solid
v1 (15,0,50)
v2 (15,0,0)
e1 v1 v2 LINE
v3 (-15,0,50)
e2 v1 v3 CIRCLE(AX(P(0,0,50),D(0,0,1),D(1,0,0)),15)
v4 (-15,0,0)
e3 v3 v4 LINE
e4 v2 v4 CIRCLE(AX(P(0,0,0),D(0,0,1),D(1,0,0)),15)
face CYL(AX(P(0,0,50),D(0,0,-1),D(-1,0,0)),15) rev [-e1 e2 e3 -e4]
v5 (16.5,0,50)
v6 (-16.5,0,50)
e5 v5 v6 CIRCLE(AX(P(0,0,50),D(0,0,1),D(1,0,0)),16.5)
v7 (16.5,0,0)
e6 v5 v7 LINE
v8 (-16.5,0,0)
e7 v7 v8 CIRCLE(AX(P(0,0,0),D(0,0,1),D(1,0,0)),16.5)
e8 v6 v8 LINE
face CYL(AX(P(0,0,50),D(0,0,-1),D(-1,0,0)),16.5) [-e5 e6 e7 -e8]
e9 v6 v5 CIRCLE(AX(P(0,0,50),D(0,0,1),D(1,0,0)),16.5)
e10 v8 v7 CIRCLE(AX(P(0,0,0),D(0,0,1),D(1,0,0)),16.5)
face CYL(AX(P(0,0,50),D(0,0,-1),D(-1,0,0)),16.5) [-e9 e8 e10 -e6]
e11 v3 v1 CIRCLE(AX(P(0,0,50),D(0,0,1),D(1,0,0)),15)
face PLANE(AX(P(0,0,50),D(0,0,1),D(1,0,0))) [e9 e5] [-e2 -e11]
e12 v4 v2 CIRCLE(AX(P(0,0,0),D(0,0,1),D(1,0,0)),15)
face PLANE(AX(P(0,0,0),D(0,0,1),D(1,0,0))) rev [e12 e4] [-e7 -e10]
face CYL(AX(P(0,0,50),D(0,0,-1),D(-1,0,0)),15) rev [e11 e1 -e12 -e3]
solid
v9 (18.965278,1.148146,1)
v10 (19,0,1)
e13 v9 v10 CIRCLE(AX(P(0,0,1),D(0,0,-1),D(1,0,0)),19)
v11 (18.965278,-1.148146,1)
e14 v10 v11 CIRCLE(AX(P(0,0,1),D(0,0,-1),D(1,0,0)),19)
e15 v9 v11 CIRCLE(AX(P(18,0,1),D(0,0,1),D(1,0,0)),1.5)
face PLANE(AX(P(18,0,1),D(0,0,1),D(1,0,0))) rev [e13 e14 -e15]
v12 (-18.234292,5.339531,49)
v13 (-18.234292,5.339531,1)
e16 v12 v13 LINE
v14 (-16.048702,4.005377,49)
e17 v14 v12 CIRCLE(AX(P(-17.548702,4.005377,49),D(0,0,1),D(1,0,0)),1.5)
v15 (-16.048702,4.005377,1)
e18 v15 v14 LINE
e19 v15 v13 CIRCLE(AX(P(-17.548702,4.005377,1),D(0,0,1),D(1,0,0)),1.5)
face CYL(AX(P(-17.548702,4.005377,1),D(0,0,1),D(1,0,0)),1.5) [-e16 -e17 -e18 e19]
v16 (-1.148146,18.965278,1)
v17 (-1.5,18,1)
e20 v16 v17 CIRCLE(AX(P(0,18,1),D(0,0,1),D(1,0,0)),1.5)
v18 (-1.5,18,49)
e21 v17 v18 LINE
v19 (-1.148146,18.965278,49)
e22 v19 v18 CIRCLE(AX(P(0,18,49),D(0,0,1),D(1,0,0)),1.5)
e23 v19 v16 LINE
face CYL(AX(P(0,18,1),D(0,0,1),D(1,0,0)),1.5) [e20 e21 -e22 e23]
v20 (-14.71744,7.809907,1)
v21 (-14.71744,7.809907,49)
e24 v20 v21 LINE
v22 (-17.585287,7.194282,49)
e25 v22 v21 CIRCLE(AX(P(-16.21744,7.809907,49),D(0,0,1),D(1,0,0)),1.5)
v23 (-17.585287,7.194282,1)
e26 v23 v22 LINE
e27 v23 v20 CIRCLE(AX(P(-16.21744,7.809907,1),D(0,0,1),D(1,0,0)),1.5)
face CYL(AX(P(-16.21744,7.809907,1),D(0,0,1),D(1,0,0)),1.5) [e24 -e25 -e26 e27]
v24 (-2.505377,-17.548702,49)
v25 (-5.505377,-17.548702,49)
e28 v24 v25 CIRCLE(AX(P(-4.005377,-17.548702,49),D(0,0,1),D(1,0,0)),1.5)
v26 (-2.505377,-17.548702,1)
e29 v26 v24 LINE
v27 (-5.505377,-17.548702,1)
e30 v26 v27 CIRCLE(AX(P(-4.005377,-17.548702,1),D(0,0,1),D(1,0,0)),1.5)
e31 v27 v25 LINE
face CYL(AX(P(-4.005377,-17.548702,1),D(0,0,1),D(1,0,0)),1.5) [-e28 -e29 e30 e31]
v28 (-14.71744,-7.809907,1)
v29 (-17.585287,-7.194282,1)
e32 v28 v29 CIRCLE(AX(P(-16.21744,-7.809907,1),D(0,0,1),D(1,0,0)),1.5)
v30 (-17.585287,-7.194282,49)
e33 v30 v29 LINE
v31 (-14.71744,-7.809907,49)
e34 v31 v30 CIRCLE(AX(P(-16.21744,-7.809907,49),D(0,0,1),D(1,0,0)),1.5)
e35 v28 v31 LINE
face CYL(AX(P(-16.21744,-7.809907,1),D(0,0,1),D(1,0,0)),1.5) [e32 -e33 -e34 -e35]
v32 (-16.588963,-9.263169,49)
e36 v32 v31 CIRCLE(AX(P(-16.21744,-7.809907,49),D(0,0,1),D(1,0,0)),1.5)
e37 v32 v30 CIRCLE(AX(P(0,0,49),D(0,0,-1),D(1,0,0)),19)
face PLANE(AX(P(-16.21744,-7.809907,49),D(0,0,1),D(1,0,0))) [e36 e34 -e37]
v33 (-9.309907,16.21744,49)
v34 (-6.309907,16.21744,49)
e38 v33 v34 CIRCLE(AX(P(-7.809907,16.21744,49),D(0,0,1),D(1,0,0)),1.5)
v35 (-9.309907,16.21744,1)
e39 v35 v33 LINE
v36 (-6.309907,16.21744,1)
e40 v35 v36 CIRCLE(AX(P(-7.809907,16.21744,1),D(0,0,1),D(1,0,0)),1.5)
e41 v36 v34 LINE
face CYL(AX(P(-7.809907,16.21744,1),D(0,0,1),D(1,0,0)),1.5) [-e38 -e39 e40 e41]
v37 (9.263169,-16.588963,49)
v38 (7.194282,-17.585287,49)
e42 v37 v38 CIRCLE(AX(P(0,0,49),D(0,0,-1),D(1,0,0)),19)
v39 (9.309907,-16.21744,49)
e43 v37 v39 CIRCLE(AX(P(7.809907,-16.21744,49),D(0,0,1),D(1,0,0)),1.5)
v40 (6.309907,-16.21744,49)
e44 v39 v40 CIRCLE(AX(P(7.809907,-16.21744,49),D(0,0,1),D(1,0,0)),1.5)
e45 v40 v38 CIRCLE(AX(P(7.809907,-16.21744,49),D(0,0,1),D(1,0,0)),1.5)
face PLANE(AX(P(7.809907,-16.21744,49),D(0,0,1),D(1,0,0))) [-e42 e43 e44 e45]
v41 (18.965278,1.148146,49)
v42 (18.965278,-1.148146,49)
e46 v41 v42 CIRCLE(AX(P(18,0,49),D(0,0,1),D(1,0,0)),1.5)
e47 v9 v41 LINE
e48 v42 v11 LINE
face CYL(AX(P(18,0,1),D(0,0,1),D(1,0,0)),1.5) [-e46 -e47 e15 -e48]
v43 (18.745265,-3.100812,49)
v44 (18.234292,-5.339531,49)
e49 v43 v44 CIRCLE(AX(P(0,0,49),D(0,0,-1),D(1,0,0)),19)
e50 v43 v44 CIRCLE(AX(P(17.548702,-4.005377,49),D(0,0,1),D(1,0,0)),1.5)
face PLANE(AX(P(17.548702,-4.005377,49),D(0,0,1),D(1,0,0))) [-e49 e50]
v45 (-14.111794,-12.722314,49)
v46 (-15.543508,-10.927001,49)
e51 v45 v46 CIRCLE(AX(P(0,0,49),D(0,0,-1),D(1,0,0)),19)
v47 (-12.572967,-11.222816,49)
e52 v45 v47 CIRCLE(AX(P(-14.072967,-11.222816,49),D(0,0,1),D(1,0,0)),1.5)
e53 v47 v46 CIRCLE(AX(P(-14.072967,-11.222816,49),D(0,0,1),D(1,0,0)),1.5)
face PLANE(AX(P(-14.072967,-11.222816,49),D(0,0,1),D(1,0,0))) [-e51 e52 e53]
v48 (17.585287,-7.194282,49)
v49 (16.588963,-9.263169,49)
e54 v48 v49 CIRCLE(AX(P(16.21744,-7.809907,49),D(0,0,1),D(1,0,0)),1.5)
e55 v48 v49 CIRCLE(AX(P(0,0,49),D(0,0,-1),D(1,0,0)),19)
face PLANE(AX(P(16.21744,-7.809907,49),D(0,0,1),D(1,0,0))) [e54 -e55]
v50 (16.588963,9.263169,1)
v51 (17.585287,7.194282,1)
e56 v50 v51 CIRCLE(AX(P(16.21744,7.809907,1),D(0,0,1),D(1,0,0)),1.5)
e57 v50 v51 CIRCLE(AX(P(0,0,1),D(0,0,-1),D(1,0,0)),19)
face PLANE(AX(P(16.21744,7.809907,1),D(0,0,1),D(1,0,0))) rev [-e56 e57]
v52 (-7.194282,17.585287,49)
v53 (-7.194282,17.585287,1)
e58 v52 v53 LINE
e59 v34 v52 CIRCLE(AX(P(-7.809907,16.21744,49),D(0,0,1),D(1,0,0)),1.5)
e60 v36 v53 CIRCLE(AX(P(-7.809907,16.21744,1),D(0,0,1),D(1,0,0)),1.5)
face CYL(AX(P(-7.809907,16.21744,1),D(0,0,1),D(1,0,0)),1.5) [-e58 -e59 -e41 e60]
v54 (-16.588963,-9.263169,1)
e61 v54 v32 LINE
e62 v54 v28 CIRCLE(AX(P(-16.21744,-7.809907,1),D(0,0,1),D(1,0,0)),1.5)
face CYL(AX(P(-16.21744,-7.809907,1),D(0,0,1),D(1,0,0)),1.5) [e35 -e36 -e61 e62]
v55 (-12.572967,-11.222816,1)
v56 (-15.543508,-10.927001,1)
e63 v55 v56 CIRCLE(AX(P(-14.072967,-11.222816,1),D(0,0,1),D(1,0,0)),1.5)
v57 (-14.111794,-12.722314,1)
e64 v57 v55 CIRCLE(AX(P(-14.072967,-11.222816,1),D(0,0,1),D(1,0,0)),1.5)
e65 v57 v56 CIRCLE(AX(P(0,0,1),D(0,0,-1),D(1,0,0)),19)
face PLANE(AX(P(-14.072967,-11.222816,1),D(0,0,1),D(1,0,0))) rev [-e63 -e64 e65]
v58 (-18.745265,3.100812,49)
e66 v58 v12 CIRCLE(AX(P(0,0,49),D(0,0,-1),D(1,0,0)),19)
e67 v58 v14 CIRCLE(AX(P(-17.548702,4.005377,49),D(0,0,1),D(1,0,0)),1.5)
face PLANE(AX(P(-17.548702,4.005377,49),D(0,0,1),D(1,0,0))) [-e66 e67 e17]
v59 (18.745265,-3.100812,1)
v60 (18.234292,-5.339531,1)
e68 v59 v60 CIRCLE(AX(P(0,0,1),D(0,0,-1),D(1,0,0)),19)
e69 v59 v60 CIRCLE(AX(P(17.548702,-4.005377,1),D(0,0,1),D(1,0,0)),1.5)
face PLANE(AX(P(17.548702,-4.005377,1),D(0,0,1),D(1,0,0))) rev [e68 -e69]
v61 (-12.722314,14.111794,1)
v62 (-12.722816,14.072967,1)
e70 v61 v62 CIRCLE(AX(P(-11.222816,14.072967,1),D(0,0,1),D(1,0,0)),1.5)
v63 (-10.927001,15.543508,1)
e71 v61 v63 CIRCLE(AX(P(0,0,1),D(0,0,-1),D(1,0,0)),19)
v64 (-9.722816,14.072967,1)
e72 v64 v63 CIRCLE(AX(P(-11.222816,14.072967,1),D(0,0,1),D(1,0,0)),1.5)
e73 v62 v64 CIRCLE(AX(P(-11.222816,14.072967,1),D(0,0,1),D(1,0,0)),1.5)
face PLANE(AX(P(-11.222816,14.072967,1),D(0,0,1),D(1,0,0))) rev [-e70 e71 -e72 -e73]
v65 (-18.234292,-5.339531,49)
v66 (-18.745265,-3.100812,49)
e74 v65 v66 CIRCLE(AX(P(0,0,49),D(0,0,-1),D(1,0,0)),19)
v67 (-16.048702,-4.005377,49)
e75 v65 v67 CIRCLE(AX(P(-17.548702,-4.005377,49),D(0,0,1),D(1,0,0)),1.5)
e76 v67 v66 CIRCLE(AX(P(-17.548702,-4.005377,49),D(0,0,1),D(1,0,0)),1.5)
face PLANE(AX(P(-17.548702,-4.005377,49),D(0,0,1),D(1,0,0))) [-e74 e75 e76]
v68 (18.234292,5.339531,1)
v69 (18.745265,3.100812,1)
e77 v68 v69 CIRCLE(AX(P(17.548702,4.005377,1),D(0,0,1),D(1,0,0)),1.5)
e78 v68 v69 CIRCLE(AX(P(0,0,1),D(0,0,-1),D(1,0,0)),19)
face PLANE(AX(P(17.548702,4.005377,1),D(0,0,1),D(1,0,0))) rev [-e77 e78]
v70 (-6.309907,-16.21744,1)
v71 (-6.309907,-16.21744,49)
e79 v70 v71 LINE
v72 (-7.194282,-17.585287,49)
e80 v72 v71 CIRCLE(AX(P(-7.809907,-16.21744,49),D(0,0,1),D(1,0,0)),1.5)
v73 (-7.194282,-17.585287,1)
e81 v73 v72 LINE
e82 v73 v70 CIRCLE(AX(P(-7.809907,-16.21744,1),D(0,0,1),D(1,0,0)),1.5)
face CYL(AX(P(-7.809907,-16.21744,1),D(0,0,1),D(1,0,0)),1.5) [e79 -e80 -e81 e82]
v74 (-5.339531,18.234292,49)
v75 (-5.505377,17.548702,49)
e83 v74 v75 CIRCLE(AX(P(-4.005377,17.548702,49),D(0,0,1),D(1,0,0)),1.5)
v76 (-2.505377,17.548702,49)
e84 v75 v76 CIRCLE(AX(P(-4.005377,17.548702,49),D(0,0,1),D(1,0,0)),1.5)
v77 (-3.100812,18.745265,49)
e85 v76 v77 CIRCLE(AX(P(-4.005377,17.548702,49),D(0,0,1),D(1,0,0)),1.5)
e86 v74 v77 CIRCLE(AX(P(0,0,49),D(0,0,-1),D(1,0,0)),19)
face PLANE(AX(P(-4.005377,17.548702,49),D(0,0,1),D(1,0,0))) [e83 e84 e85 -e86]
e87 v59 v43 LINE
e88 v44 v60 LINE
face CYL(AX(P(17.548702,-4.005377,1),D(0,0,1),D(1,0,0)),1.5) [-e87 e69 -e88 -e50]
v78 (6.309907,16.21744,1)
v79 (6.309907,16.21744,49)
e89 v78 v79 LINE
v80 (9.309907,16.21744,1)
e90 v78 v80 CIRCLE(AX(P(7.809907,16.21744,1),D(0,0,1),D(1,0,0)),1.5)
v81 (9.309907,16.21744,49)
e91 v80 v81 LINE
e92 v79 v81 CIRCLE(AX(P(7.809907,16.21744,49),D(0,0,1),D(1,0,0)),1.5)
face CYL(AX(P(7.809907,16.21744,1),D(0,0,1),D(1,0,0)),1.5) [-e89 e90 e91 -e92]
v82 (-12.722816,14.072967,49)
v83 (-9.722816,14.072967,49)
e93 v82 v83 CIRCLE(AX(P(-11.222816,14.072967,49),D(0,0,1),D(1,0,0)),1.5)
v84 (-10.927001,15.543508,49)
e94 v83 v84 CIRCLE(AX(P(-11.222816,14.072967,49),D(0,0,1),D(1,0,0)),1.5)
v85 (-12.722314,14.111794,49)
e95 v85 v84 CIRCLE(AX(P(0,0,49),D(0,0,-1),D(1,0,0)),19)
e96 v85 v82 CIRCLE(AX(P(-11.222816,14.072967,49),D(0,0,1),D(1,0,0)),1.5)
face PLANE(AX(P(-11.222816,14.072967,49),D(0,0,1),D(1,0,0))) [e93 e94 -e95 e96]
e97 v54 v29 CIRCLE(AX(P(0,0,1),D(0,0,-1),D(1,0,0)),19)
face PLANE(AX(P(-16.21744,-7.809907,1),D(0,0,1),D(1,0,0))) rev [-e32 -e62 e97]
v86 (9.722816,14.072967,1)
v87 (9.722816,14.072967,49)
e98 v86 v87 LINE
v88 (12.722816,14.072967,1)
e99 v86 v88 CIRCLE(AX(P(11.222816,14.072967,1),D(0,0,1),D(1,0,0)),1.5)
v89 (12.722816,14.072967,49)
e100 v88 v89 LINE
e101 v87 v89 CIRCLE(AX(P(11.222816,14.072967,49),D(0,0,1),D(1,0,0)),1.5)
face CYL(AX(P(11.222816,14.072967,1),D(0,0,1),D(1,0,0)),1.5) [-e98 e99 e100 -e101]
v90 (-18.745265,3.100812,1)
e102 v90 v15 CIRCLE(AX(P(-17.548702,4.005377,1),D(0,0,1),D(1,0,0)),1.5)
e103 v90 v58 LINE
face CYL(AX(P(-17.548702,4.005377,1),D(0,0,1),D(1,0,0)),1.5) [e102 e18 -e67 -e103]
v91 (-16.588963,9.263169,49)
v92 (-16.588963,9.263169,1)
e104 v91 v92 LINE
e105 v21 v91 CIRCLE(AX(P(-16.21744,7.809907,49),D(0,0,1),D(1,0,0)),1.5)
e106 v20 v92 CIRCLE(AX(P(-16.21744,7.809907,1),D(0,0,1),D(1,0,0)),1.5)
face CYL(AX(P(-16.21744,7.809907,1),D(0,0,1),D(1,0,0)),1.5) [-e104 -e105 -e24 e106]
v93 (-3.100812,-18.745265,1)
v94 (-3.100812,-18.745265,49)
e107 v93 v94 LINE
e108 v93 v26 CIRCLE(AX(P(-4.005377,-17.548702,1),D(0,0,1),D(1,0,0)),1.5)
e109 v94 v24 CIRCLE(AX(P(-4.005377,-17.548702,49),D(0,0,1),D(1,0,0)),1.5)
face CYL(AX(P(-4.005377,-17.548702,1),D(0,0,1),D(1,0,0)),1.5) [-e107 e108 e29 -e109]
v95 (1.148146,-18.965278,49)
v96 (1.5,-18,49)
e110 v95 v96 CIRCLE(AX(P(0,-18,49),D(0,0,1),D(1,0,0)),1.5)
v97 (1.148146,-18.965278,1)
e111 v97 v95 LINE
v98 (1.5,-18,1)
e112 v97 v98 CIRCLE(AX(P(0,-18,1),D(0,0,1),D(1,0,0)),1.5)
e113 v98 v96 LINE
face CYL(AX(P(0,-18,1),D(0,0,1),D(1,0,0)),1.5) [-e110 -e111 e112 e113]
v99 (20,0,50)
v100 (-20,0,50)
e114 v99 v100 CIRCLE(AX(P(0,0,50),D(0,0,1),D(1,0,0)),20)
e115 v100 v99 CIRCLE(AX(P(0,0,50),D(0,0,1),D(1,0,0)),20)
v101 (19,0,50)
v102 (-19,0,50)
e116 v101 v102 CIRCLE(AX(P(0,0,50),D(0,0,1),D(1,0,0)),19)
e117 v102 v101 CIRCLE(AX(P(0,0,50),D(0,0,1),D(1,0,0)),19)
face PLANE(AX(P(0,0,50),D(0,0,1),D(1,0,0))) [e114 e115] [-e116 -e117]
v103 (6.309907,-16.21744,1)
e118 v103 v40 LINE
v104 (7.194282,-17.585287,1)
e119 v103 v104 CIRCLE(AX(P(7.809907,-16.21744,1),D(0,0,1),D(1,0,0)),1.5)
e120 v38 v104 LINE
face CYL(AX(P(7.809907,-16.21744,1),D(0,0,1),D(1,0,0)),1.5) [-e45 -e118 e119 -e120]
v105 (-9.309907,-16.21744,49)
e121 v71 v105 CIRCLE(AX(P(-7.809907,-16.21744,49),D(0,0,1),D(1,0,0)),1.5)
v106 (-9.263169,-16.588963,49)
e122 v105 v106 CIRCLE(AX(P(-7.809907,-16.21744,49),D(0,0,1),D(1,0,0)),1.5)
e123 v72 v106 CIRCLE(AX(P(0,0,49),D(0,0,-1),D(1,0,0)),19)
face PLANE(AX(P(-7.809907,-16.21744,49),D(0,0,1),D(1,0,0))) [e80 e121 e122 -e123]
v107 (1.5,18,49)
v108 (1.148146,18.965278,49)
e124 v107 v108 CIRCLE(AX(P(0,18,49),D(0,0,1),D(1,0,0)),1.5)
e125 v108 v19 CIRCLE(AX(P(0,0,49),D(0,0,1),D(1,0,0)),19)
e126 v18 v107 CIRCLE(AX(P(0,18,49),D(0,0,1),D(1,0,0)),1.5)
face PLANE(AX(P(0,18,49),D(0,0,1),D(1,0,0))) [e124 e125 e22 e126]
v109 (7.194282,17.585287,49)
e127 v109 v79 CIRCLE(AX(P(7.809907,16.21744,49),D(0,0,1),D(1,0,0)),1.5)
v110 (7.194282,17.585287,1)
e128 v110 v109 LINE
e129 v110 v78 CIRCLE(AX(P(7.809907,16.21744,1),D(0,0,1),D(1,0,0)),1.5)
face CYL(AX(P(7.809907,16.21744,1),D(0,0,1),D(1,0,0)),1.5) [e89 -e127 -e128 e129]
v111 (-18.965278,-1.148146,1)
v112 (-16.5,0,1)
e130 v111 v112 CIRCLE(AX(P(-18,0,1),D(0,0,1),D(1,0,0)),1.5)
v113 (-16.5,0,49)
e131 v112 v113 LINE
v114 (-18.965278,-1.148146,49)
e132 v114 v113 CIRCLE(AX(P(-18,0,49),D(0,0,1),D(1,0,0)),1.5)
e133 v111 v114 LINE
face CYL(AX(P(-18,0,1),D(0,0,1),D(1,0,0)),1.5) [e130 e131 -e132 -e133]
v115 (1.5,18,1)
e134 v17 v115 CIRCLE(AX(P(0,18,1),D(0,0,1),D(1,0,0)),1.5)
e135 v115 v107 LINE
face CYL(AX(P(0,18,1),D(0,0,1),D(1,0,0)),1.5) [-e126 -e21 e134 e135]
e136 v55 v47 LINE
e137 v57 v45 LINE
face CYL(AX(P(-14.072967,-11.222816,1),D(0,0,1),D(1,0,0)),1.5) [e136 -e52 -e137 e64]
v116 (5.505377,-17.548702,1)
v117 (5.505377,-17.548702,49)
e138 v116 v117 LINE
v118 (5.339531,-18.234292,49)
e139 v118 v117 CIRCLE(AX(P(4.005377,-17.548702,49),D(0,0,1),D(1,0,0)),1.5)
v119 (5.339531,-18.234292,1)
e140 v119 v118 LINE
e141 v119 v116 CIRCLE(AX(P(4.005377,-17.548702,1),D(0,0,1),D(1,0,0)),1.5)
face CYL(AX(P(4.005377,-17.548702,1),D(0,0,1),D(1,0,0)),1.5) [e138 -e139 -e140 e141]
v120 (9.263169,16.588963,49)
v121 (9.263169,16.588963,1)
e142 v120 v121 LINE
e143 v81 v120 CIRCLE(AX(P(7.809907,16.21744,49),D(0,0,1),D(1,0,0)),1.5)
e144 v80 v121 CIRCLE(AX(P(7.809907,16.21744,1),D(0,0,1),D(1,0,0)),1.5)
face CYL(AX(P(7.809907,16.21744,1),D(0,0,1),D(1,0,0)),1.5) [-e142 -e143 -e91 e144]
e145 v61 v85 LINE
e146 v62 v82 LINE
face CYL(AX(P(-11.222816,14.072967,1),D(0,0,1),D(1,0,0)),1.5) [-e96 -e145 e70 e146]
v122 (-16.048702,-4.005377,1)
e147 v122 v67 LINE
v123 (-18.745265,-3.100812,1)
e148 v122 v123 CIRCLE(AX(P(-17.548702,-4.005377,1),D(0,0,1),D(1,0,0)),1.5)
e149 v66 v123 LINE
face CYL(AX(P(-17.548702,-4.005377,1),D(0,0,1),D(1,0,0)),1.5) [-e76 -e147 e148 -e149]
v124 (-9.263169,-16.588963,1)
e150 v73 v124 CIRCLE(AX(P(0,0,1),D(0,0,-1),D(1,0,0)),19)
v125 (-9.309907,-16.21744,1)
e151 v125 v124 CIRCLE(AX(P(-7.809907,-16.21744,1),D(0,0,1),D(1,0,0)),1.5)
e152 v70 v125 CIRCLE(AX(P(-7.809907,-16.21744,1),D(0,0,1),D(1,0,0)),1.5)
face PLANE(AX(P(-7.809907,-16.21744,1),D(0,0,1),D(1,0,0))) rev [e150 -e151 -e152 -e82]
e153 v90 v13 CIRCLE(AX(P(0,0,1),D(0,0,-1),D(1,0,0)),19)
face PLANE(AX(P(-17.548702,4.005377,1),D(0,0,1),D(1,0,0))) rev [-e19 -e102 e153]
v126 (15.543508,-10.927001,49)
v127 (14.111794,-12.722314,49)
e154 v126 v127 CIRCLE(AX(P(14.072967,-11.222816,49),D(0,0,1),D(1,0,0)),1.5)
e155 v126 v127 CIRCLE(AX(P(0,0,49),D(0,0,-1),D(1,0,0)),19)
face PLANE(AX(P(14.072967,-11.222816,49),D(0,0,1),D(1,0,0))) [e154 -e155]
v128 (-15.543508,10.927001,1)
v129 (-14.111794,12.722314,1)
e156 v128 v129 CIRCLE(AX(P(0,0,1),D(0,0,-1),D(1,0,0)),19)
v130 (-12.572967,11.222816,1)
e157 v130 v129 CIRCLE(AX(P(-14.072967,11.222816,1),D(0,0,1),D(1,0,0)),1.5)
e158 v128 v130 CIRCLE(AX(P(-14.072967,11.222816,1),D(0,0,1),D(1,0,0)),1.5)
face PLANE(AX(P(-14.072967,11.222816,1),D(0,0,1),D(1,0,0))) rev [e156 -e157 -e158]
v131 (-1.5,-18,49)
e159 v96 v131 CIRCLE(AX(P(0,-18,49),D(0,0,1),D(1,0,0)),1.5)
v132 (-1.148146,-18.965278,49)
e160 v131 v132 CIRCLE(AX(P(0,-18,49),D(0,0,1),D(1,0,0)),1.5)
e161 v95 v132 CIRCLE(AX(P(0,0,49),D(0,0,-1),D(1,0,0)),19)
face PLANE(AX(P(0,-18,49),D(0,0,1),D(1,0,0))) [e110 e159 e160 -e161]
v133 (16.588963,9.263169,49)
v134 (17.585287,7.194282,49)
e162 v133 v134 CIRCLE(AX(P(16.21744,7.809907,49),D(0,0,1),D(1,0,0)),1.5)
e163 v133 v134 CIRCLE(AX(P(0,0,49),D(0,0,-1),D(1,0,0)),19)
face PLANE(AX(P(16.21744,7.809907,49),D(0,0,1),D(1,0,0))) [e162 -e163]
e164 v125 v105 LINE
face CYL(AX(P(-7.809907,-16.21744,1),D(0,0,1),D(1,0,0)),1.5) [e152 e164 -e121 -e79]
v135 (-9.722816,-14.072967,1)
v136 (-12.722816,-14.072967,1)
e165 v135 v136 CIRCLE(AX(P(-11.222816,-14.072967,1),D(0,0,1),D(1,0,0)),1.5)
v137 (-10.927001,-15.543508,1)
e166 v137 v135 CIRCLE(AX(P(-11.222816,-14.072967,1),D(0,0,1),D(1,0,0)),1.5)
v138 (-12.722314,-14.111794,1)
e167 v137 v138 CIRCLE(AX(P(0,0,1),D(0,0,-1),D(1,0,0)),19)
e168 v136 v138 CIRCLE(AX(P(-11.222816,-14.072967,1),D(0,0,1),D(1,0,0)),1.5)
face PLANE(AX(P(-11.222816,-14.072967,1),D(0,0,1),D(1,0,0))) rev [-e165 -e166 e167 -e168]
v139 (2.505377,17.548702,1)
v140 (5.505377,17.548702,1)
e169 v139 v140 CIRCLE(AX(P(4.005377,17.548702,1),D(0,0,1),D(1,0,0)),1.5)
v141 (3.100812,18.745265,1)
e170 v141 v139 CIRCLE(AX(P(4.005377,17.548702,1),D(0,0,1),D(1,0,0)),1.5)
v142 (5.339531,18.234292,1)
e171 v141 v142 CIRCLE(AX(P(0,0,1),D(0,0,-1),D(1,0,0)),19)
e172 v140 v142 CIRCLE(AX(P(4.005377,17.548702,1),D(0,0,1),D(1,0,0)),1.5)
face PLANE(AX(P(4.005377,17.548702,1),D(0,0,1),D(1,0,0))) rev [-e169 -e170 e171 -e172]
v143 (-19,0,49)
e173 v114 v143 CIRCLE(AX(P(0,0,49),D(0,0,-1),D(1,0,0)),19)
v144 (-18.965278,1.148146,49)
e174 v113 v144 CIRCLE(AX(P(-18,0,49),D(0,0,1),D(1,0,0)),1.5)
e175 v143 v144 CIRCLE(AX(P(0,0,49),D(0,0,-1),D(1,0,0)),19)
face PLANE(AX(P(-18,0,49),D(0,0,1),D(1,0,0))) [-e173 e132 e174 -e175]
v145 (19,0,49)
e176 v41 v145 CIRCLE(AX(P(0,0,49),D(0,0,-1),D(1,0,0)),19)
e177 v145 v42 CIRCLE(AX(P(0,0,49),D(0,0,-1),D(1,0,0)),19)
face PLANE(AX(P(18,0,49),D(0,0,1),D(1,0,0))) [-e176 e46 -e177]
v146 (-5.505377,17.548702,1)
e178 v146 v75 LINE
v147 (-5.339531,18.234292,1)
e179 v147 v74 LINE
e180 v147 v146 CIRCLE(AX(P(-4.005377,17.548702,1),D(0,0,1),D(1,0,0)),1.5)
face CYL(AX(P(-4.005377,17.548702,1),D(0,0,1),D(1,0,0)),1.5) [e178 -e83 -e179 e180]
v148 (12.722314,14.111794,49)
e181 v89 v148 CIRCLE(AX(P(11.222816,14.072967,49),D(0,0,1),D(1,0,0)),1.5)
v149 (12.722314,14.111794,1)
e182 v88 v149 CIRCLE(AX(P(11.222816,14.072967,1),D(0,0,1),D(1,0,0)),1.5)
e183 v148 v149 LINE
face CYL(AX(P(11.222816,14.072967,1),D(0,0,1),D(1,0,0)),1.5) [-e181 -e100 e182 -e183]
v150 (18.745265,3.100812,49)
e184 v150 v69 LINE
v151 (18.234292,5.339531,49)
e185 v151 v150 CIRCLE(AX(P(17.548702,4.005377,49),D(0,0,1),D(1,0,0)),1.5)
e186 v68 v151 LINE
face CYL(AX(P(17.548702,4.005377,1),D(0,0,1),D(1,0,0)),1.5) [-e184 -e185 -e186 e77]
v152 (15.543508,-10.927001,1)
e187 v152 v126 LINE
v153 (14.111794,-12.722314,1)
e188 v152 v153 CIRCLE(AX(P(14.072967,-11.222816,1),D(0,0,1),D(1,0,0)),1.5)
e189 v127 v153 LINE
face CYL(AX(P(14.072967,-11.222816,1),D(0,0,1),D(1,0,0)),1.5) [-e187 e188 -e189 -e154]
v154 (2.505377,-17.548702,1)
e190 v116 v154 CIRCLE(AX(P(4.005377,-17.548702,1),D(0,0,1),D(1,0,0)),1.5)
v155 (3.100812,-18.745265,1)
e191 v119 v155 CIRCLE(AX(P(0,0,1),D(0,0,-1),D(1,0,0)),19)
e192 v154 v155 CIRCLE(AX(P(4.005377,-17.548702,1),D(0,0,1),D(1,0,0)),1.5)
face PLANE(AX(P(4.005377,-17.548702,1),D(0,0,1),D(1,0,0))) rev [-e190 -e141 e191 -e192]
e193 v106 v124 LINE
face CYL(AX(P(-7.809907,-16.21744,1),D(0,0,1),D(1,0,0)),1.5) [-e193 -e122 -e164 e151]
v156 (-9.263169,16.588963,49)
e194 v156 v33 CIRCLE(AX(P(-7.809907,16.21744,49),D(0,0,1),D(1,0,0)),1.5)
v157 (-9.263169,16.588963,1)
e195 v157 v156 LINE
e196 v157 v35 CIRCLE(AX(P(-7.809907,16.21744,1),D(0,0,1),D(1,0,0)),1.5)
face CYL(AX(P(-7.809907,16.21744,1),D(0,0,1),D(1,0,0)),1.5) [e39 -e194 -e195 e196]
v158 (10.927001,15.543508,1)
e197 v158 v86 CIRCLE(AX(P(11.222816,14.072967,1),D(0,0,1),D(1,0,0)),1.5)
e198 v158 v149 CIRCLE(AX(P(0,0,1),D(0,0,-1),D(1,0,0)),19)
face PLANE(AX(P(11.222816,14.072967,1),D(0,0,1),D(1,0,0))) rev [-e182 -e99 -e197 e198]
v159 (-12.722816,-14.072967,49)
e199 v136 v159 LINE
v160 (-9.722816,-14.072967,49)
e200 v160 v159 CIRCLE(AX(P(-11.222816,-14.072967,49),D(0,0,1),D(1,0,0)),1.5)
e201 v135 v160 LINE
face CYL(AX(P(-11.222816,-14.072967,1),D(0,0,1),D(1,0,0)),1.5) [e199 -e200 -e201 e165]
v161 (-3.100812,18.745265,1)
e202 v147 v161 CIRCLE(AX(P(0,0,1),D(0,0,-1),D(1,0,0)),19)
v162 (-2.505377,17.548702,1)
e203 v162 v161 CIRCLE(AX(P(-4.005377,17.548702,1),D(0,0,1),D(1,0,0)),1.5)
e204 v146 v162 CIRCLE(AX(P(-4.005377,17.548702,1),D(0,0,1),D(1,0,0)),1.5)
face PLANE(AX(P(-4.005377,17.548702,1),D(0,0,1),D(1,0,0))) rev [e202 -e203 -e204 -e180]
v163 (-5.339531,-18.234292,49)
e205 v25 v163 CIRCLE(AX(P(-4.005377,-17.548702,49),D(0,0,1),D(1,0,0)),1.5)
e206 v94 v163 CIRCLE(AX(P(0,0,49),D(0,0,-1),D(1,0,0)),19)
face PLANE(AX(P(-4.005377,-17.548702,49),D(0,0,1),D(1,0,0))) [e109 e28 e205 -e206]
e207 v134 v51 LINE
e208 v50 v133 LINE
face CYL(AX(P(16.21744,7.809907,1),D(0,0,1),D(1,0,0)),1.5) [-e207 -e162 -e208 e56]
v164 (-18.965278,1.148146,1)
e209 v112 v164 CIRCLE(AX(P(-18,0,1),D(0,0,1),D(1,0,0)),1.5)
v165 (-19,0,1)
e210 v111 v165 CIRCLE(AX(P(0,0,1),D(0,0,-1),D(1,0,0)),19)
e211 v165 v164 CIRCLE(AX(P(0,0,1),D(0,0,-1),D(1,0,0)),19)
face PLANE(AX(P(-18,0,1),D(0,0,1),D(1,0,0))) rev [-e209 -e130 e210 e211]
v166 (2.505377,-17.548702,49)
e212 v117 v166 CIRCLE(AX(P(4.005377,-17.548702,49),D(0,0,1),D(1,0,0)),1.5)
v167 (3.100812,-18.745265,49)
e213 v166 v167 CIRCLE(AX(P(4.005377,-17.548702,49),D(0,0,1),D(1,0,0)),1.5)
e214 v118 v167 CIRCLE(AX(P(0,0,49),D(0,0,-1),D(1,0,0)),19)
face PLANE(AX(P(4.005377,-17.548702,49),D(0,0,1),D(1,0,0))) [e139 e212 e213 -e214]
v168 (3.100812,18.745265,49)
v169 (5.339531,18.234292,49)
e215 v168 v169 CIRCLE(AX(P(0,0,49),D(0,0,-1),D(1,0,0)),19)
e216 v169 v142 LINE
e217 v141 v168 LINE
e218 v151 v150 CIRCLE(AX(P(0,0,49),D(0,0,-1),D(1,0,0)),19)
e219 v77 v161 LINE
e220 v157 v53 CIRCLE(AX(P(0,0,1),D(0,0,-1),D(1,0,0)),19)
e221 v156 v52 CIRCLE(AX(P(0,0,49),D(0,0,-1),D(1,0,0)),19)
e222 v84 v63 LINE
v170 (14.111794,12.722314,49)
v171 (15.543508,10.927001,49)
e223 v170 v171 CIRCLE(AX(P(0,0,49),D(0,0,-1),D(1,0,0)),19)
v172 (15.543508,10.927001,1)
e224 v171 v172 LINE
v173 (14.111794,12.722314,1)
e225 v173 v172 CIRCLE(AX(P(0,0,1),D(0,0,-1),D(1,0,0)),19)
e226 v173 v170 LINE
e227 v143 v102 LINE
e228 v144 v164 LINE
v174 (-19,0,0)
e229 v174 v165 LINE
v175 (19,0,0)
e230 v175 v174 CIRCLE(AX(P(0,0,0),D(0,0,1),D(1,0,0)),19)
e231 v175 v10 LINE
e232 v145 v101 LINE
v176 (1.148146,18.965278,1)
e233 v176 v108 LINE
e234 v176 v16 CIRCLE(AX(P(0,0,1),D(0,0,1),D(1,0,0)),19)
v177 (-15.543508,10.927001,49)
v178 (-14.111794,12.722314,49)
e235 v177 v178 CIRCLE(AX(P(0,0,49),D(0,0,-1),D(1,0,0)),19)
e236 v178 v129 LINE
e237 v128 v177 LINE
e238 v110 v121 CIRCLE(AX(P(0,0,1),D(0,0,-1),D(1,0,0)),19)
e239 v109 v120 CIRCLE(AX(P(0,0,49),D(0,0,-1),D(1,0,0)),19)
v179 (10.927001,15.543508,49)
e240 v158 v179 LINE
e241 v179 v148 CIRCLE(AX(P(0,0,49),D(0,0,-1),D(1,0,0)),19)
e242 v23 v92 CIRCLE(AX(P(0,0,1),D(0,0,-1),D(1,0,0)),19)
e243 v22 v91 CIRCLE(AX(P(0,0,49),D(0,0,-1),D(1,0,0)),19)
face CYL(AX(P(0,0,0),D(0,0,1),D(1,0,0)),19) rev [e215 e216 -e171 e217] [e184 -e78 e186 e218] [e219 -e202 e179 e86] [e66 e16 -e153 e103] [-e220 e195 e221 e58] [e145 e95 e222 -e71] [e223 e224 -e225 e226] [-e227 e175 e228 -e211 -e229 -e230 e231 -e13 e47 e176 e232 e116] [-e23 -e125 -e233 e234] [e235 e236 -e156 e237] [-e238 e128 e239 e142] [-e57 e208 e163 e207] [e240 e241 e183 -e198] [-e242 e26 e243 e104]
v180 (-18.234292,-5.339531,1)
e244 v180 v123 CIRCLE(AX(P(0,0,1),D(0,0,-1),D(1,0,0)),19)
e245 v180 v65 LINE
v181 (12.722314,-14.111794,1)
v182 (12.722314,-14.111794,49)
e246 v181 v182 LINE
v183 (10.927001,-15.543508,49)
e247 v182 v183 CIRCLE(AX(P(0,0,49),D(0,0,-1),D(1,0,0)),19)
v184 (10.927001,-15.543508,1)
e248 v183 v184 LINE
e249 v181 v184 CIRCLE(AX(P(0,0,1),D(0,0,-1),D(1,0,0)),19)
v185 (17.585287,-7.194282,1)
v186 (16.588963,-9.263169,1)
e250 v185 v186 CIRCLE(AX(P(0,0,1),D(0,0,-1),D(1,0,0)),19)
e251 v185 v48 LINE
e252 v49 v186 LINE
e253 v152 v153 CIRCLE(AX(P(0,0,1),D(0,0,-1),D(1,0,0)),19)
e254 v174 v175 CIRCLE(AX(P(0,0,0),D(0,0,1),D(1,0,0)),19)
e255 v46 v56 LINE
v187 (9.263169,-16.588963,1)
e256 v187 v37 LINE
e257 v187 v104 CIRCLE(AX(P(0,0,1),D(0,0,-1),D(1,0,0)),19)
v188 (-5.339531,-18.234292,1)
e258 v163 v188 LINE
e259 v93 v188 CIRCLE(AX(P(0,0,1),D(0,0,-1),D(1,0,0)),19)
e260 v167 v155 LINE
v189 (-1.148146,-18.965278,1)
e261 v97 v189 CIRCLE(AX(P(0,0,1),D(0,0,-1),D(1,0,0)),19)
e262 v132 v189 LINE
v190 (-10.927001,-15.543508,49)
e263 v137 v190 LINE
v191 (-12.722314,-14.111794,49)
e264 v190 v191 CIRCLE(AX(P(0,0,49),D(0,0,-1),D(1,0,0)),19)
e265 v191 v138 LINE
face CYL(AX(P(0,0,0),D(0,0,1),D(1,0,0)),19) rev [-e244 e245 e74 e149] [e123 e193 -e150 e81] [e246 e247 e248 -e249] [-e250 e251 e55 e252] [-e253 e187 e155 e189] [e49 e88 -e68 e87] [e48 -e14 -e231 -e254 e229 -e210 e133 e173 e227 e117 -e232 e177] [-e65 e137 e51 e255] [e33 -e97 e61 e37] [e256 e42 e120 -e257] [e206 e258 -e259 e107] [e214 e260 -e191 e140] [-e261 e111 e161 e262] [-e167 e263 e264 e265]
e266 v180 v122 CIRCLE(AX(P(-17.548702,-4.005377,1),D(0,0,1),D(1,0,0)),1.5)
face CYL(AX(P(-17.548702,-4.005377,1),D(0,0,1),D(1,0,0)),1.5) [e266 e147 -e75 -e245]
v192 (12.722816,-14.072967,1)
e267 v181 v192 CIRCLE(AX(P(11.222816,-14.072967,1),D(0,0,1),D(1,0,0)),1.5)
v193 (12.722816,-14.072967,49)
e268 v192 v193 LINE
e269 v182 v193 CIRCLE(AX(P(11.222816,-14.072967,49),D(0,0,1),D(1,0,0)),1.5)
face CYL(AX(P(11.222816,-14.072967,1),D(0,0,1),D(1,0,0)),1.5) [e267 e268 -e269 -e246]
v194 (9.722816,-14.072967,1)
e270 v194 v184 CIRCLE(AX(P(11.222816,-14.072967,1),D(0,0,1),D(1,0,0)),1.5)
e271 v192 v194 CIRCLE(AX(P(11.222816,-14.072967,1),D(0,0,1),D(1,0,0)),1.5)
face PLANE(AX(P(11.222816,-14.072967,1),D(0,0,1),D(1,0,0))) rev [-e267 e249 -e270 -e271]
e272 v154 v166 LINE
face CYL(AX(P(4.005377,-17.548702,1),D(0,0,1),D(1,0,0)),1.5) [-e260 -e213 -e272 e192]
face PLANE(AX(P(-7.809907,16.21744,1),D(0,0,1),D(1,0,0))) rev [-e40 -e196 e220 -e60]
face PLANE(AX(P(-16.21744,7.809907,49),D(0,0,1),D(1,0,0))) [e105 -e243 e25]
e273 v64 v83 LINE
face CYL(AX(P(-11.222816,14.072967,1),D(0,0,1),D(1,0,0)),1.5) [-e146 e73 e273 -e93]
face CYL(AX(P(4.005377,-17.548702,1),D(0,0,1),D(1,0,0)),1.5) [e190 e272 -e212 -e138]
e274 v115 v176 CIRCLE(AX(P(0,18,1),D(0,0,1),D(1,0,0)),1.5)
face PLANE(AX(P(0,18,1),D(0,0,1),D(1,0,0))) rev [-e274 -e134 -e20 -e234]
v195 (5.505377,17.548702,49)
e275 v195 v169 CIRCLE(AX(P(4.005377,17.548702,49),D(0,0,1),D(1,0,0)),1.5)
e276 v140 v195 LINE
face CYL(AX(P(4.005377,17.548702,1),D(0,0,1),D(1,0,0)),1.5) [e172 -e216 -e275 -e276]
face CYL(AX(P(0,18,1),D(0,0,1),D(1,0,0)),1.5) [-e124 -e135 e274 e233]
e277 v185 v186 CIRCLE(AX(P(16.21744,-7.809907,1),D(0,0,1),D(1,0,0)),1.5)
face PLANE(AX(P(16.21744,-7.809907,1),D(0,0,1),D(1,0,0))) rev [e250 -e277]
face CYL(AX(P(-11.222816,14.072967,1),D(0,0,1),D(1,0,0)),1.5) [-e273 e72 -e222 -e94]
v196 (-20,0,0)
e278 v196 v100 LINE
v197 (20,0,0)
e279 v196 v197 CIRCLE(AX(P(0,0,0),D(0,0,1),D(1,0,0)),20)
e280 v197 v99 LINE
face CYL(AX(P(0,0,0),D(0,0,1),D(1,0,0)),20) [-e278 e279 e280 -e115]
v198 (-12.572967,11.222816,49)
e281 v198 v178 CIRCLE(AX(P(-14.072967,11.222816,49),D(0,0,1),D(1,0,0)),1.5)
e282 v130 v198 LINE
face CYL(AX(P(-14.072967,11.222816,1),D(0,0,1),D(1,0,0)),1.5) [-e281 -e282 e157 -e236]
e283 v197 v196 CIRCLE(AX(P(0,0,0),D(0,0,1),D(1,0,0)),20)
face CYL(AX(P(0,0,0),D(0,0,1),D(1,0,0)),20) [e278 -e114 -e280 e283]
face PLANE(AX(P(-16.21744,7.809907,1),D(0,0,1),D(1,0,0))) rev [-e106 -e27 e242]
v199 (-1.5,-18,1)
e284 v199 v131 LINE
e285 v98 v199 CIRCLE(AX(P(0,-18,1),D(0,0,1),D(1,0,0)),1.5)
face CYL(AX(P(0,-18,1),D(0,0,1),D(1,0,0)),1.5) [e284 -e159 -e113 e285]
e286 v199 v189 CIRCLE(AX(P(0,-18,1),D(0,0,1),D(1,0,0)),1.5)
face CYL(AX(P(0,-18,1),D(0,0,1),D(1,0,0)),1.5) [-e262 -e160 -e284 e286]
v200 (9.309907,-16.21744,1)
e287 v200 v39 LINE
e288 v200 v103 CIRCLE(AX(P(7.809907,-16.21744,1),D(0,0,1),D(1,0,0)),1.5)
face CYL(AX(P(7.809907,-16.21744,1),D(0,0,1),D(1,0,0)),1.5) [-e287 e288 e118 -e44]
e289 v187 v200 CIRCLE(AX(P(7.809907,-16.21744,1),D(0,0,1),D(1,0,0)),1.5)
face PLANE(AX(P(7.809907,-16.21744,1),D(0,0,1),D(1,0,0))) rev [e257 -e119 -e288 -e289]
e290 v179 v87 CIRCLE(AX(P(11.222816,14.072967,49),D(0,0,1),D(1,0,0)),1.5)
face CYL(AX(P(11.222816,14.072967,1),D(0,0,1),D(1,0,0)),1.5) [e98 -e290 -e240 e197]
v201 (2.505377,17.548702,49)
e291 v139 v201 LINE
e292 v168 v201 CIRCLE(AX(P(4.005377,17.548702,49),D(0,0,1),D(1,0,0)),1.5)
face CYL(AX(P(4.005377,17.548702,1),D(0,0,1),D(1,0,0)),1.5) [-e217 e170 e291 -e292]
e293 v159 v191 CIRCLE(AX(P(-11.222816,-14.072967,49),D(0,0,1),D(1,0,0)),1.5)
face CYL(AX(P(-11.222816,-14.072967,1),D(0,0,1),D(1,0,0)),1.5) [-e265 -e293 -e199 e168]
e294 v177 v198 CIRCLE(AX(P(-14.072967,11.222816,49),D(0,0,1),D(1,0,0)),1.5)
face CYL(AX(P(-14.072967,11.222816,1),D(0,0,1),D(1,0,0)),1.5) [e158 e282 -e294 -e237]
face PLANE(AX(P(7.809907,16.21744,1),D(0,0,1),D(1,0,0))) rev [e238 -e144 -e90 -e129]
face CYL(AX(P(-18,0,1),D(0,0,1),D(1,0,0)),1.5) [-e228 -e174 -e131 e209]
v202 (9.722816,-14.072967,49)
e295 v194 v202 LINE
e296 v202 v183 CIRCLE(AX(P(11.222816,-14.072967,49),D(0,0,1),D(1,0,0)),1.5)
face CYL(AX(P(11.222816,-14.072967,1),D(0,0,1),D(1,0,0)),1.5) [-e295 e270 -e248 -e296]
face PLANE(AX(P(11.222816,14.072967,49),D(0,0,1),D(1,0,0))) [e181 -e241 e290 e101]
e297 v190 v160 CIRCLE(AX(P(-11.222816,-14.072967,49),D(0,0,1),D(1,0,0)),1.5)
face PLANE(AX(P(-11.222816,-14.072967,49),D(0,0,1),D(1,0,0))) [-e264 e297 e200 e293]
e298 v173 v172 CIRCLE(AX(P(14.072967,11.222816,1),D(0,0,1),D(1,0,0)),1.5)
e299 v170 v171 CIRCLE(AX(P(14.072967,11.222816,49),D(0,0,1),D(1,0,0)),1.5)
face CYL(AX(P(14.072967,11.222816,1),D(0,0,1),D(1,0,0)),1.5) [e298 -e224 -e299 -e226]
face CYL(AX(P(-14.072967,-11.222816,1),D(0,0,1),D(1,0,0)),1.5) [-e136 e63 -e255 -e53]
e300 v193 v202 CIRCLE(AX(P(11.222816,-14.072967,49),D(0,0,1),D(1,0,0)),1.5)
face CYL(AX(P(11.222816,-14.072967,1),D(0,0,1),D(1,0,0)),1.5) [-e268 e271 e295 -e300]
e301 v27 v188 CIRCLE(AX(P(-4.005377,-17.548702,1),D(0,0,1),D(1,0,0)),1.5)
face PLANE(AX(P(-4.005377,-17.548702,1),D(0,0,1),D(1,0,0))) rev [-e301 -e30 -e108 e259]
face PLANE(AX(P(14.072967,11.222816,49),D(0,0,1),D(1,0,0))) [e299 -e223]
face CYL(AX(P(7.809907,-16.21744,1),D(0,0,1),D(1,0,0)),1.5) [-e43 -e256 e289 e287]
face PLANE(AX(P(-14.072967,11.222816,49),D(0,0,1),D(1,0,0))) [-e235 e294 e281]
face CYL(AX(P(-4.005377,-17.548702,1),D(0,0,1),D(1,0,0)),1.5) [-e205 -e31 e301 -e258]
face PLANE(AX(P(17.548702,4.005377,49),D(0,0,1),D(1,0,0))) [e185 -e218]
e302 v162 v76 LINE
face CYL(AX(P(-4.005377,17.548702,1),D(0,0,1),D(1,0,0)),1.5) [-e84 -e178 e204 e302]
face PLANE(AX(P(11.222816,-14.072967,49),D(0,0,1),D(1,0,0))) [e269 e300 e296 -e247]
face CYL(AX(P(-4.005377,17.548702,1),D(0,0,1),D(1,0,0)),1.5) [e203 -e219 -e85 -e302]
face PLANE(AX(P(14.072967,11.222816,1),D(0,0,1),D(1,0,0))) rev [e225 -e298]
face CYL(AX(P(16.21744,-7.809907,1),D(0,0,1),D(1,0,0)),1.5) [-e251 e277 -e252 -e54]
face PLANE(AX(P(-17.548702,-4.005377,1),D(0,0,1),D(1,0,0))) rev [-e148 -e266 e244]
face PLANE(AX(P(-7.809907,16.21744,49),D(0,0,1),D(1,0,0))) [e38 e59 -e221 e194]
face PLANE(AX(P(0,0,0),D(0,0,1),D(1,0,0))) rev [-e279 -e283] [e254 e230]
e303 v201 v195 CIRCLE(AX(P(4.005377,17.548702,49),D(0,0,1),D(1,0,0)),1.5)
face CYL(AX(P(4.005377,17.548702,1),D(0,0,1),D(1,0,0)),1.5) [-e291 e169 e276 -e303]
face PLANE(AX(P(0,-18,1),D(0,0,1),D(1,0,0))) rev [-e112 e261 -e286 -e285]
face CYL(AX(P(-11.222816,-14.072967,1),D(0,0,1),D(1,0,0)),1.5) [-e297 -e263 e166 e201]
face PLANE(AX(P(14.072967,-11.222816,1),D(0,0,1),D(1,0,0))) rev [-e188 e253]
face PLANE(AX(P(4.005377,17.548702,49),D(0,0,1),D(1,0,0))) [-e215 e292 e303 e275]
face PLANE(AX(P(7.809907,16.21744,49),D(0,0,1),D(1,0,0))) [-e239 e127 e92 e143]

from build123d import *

# Parameters (mm, degrees)
SKETCH1_R              = 16.5
SKETCH1_R_2            = 15
BOSS_EXTRUDE1_DEPTH    = 50
BOSS_EXTRUDE2_START    = -1
SKETCH2_R              = 1.5
BOSS_EXTRUDE2_DEPTH    = 48
BOSS_EXTRUDE2_2_DEPTH  = 48
BOSS_EXTRUDE2_3_DEPTH  = 48
BOSS_EXTRUDE2_4_DEPTH  = 48
BOSS_EXTRUDE2_5_DEPTH  = 48
BOSS_EXTRUDE2_6_DEPTH  = 48
BOSS_EXTRUDE2_7_DEPTH  = 48
BOSS_EXTRUDE2_8_DEPTH  = 48
BOSS_EXTRUDE2_9_DEPTH  = 48
BOSS_EXTRUDE2_10_DEPTH = 48
BOSS_EXTRUDE2_11_DEPTH = 48
BOSS_EXTRUDE2_12_DEPTH = 48
BOSS_EXTRUDE2_13_DEPTH = 48
BOSS_EXTRUDE2_14_DEPTH = 48
BOSS_EXTRUDE2_15_DEPTH = 48
BOSS_EXTRUDE2_16_DEPTH = 48
BOSS_EXTRUDE2_17_DEPTH = 48
BOSS_EXTRUDE2_18_DEPTH = 48
BOSS_EXTRUDE2_19_DEPTH = 48
BOSS_EXTRUDE2_20_DEPTH = 48
BOSS_EXTRUDE2_21_DEPTH = 48
BOSS_EXTRUDE2_22_DEPTH = 48
BOSS_EXTRUDE2_23_DEPTH = 48
BOSS_EXTRUDE2_24_DEPTH = 48
BOSS_EXTRUDE2_25_DEPTH = 48
BOSS_EXTRUDE2_26_DEPTH = 48
BOSS_EXTRUDE2_27_DEPTH = 48
BOSS_EXTRUDE2_28_DEPTH = 48
SKETCH3_R              = 20
SKETCH3_R_2            = 19
BOSS_EXTRUDE3_DEPTH    = 50


with BuildPart() as part:
    # Sketch1 → Boss-Extrude1 (new body)
    with BuildSketch(Plane.XY):
        Circle(SKETCH1_R)
        Circle(SKETCH1_R_2, mode=Mode.SUBTRACT)
    extrude(amount=BOSS_EXTRUDE1_DEPTH)


with BuildPart() as body_2:
    # Sketch2 → Boss-Extrude2 (new body)
    with BuildSketch(Plane.XY.offset(50).offset(BOSS_EXTRUDE2_START)):
        with Locations((0, 18)):
            Circle(SKETCH2_R)
    extrude(amount=-BOSS_EXTRUDE2_DEPTH)



with BuildPart() as body_3:
    # Sketch2 → Boss-Extrude2 2 (new body)
    with BuildSketch(Plane.XY.offset(50).offset(BOSS_EXTRUDE2_START)):
        with Locations((4.005376811, 17.548702419)):
            Circle(SKETCH2_R)
    extrude(amount=-BOSS_EXTRUDE2_2_DEPTH)


with BuildPart() as body_4:
    # Sketch2 → Boss-Extrude2 3 (new body)
    with BuildSketch(Plane.XY.offset(50).offset(BOSS_EXTRUDE2_START)):
        with Locations((7.809907304, 16.217439622)):
            Circle(SKETCH2_R)
    extrude(amount=-BOSS_EXTRUDE2_3_DEPTH)


with BuildPart() as body_5:
    # Sketch2 → Boss-Extrude2 4 (new body)
    with BuildSketch(Plane.XY.offset(50).offset(BOSS_EXTRUDE2_START)):
        with Locations((11.222816433, 14.072966684)):
            Circle(SKETCH2_R)
    extrude(amount=-BOSS_EXTRUDE2_4_DEPTH)


with BuildPart() as body_6:
    # Sketch2 → Boss-Extrude2 5 (new body)
    with BuildSketch(Plane.XY.offset(50).offset(BOSS_EXTRUDE2_START)):
        with Locations((14.072966684, 11.222816433)):
            Circle(SKETCH2_R)
    extrude(amount=-BOSS_EXTRUDE2_5_DEPTH)


with BuildPart() as body_7:
    # Sketch2 → Boss-Extrude2 6 (new body)
    with BuildSketch(Plane.XY.offset(50).offset(BOSS_EXTRUDE2_START)):
        with Locations((16.217439622, 7.809907304)):
            Circle(SKETCH2_R)
    extrude(amount=-BOSS_EXTRUDE2_6_DEPTH)


with BuildPart() as body_8:
    # Sketch2 → Boss-Extrude2 7 (new body)
    with BuildSketch(Plane.XY.offset(50).offset(BOSS_EXTRUDE2_START)):
        with Locations((17.548702419, 4.005376811)):
            Circle(SKETCH2_R)
    extrude(amount=-BOSS_EXTRUDE2_7_DEPTH)


with BuildPart() as body_9:
    # Sketch2 → Boss-Extrude2 8 (new body)
    with BuildSketch(Plane.XY.offset(50).offset(BOSS_EXTRUDE2_START)):
        with Locations((18, 0)):
            Circle(SKETCH2_R)
    extrude(amount=-BOSS_EXTRUDE2_8_DEPTH)


with BuildPart() as body_10:
    # Sketch2 → Boss-Extrude2 9 (new body)
    with BuildSketch(Plane.XY.offset(50).offset(BOSS_EXTRUDE2_START)):
        with Locations((17.548702419, -4.005376811)):
            Circle(SKETCH2_R)
    extrude(amount=-BOSS_EXTRUDE2_9_DEPTH)


with BuildPart() as body_11:
    # Sketch2 → Boss-Extrude2 10 (new body)
    with BuildSketch(Plane.XY.offset(50).offset(BOSS_EXTRUDE2_START)):
        with Locations((16.217439622, -7.809907304)):
            Circle(SKETCH2_R)
    extrude(amount=-BOSS_EXTRUDE2_10_DEPTH)


with BuildPart() as body_12:
    # Sketch2 → Boss-Extrude2 11 (new body)
    with BuildSketch(Plane.XY.offset(50).offset(BOSS_EXTRUDE2_START)):
        with Locations((14.072966684, -11.222816433)):
            Circle(SKETCH2_R)
    extrude(amount=-BOSS_EXTRUDE2_11_DEPTH)


with BuildPart() as body_13:
    # Sketch2 → Boss-Extrude2 12 (new body)
    with BuildSketch(Plane.XY.offset(50).offset(BOSS_EXTRUDE2_START)):
        with Locations((11.222816433, -14.072966684)):
            Circle(SKETCH2_R)
    extrude(amount=-BOSS_EXTRUDE2_12_DEPTH)


with BuildPart() as body_14:
    # Sketch2 → Boss-Extrude2 13 (new body)
    with BuildSketch(Plane.XY.offset(50).offset(BOSS_EXTRUDE2_START)):
        with Locations((7.809907304, -16.217439622)):
            Circle(SKETCH2_R)
    extrude(amount=-BOSS_EXTRUDE2_13_DEPTH)


with BuildPart() as body_15:
    # Sketch2 → Boss-Extrude2 14 (new body)
    with BuildSketch(Plane.XY.offset(50).offset(BOSS_EXTRUDE2_START)):
        with Locations((4.005376811, -17.548702419)):
            Circle(SKETCH2_R)
    extrude(amount=-BOSS_EXTRUDE2_14_DEPTH)


with BuildPart() as body_16:
    # Sketch2 → Boss-Extrude2 15 (new body)
    with BuildSketch(Plane.XY.offset(50).offset(BOSS_EXTRUDE2_START)):
        with Locations((0, -18)):
            Circle(SKETCH2_R)
    extrude(amount=-BOSS_EXTRUDE2_15_DEPTH)


with BuildPart() as body_17:
    # Sketch2 → Boss-Extrude2 16 (new body)
    with BuildSketch(Plane.XY.offset(50).offset(BOSS_EXTRUDE2_START)):
        with Locations((-4.005376811, -17.548702419)):
            Circle(SKETCH2_R)
    extrude(amount=-BOSS_EXTRUDE2_16_DEPTH)


with BuildPart() as body_18:
    # Sketch2 → Boss-Extrude2 17 (new body)
    with BuildSketch(Plane.XY.offset(50).offset(BOSS_EXTRUDE2_START)):
        with Locations((-7.809907304, -16.217439622)):
            Circle(SKETCH2_R)
    extrude(amount=-BOSS_EXTRUDE2_17_DEPTH)


with BuildPart() as body_19:
    # Sketch2 → Boss-Extrude2 18 (new body)
    with BuildSketch(Plane.XY.offset(50).offset(BOSS_EXTRUDE2_START)):
        with Locations((-11.222816433, -14.072966684)):
            Circle(SKETCH2_R)
    extrude(amount=-BOSS_EXTRUDE2_18_DEPTH)


with BuildPart() as body_20:
    # Sketch2 → Boss-Extrude2 19 (new body)
    with BuildSketch(Plane.XY.offset(50).offset(BOSS_EXTRUDE2_START)):
        with Locations((-14.072966684, -11.222816433)):
            Circle(SKETCH2_R)
    extrude(amount=-BOSS_EXTRUDE2_19_DEPTH)


with BuildPart() as body_21:
    # Sketch2 → Boss-Extrude2 20 (new body)
    with BuildSketch(Plane.XY.offset(50).offset(BOSS_EXTRUDE2_START)):
        with Locations((-16.217439622, -7.809907304)):
            Circle(SKETCH2_R)
    extrude(amount=-BOSS_EXTRUDE2_20_DEPTH)


with BuildPart() as body_22:
    # Sketch2 → Boss-Extrude2 21 (new body)
    with BuildSketch(Plane.XY.offset(50).offset(BOSS_EXTRUDE2_START)):
        with Locations((-17.548702419, -4.005376811)):
            Circle(SKETCH2_R)
    extrude(amount=-BOSS_EXTRUDE2_21_DEPTH)


with BuildPart() as body_23:
    # Sketch2 → Boss-Extrude2 22 (new body)
    with BuildSketch(Plane.XY.offset(50).offset(BOSS_EXTRUDE2_START)):
        with Locations((-18, 0)):
            Circle(SKETCH2_R)
    extrude(amount=-BOSS_EXTRUDE2_22_DEPTH)


with BuildPart() as body_24:
    # Sketch2 → Boss-Extrude2 23 (new body)
    with BuildSketch(Plane.XY.offset(50).offset(BOSS_EXTRUDE2_START)):
        with Locations((-17.548702419, 4.005376811)):
            Circle(SKETCH2_R)
    extrude(amount=-BOSS_EXTRUDE2_23_DEPTH)


with BuildPart() as body_25:
    # Sketch2 → Boss-Extrude2 24 (new body)
    with BuildSketch(Plane.XY.offset(50).offset(BOSS_EXTRUDE2_START)):
        with Locations((-16.217439622, 7.809907304)):
            Circle(SKETCH2_R)
    extrude(amount=-BOSS_EXTRUDE2_24_DEPTH)


with BuildPart() as body_26:
    # Sketch2 → Boss-Extrude2 25 (new body)
    with BuildSketch(Plane.XY.offset(50).offset(BOSS_EXTRUDE2_START)):
        with Locations((-14.072966684, 11.222816433)):
            Circle(SKETCH2_R)
    extrude(amount=-BOSS_EXTRUDE2_25_DEPTH)


with BuildPart() as body_27:
    # Sketch2 → Boss-Extrude2 26 (new body)
    with BuildSketch(Plane.XY.offset(50).offset(BOSS_EXTRUDE2_START)):
        with Locations((-11.222816433, 14.072966684)):
            Circle(SKETCH2_R)
    extrude(amount=-BOSS_EXTRUDE2_26_DEPTH)


with BuildPart() as body_28:
    # Sketch2 → Boss-Extrude2 27 (new body)
    with BuildSketch(Plane.XY.offset(50).offset(BOSS_EXTRUDE2_START)):
        with Locations((-7.809907304, 16.217439622)):
            Circle(SKETCH2_R)
    extrude(amount=-BOSS_EXTRUDE2_27_DEPTH)


with BuildPart() as body_29:
    # Sketch2 → Boss-Extrude2 28 (new body)
    with BuildSketch(Plane.XY.offset(50).offset(BOSS_EXTRUDE2_START)):
        with Locations((-4.005376811, 17.548702419)):
            Circle(SKETCH2_R)
    extrude(amount=-BOSS_EXTRUDE2_28_DEPTH)


with BuildPart() as body_2_1:
    add(body_2.part)

    add(body_3.part)  # Boss-Extrude3 merges body 3

    add(body_4.part)  # Boss-Extrude3 merges body 4

    add(body_5.part)  # Boss-Extrude3 merges body 5

    add(body_6.part)  # Boss-Extrude3 merges body 6

    add(body_7.part)  # Boss-Extrude3 merges body 7

    add(body_8.part)  # Boss-Extrude3 merges body 8

    add(body_9.part)  # Boss-Extrude3 merges body 9

    add(body_10.part)  # Boss-Extrude3 merges body 10

    add(body_11.part)  # Boss-Extrude3 merges body 11

    add(body_12.part)  # Boss-Extrude3 merges body 12

    add(body_13.part)  # Boss-Extrude3 merges body 13

    add(body_14.part)  # Boss-Extrude3 merges body 14

    add(body_15.part)  # Boss-Extrude3 merges body 15

    add(body_16.part)  # Boss-Extrude3 merges body 16

    add(body_17.part)  # Boss-Extrude3 merges body 17

    add(body_18.part)  # Boss-Extrude3 merges body 18

    add(body_19.part)  # Boss-Extrude3 merges body 19

    add(body_20.part)  # Boss-Extrude3 merges body 20

    add(body_21.part)  # Boss-Extrude3 merges body 21

    add(body_22.part)  # Boss-Extrude3 merges body 22

    add(body_23.part)  # Boss-Extrude3 merges body 23

    add(body_24.part)  # Boss-Extrude3 merges body 24

    add(body_25.part)  # Boss-Extrude3 merges body 25

    add(body_26.part)  # Boss-Extrude3 merges body 26

    add(body_27.part)  # Boss-Extrude3 merges body 27

    add(body_28.part)  # Boss-Extrude3 merges body 28

    add(body_29.part)  # Boss-Extrude3 merges body 29
    # Sketch3 → Boss-Extrude3 (add)
    with BuildSketch(Plane.XY.offset(50)):
        Circle(SKETCH3_R)
        Circle(SKETCH3_R_2, mode=Mode.SUBTRACT)
    extrude(amount=-BOSS_EXTRUDE3_DEPTH)


solid = Compound([part.part, body_2_1.part])
